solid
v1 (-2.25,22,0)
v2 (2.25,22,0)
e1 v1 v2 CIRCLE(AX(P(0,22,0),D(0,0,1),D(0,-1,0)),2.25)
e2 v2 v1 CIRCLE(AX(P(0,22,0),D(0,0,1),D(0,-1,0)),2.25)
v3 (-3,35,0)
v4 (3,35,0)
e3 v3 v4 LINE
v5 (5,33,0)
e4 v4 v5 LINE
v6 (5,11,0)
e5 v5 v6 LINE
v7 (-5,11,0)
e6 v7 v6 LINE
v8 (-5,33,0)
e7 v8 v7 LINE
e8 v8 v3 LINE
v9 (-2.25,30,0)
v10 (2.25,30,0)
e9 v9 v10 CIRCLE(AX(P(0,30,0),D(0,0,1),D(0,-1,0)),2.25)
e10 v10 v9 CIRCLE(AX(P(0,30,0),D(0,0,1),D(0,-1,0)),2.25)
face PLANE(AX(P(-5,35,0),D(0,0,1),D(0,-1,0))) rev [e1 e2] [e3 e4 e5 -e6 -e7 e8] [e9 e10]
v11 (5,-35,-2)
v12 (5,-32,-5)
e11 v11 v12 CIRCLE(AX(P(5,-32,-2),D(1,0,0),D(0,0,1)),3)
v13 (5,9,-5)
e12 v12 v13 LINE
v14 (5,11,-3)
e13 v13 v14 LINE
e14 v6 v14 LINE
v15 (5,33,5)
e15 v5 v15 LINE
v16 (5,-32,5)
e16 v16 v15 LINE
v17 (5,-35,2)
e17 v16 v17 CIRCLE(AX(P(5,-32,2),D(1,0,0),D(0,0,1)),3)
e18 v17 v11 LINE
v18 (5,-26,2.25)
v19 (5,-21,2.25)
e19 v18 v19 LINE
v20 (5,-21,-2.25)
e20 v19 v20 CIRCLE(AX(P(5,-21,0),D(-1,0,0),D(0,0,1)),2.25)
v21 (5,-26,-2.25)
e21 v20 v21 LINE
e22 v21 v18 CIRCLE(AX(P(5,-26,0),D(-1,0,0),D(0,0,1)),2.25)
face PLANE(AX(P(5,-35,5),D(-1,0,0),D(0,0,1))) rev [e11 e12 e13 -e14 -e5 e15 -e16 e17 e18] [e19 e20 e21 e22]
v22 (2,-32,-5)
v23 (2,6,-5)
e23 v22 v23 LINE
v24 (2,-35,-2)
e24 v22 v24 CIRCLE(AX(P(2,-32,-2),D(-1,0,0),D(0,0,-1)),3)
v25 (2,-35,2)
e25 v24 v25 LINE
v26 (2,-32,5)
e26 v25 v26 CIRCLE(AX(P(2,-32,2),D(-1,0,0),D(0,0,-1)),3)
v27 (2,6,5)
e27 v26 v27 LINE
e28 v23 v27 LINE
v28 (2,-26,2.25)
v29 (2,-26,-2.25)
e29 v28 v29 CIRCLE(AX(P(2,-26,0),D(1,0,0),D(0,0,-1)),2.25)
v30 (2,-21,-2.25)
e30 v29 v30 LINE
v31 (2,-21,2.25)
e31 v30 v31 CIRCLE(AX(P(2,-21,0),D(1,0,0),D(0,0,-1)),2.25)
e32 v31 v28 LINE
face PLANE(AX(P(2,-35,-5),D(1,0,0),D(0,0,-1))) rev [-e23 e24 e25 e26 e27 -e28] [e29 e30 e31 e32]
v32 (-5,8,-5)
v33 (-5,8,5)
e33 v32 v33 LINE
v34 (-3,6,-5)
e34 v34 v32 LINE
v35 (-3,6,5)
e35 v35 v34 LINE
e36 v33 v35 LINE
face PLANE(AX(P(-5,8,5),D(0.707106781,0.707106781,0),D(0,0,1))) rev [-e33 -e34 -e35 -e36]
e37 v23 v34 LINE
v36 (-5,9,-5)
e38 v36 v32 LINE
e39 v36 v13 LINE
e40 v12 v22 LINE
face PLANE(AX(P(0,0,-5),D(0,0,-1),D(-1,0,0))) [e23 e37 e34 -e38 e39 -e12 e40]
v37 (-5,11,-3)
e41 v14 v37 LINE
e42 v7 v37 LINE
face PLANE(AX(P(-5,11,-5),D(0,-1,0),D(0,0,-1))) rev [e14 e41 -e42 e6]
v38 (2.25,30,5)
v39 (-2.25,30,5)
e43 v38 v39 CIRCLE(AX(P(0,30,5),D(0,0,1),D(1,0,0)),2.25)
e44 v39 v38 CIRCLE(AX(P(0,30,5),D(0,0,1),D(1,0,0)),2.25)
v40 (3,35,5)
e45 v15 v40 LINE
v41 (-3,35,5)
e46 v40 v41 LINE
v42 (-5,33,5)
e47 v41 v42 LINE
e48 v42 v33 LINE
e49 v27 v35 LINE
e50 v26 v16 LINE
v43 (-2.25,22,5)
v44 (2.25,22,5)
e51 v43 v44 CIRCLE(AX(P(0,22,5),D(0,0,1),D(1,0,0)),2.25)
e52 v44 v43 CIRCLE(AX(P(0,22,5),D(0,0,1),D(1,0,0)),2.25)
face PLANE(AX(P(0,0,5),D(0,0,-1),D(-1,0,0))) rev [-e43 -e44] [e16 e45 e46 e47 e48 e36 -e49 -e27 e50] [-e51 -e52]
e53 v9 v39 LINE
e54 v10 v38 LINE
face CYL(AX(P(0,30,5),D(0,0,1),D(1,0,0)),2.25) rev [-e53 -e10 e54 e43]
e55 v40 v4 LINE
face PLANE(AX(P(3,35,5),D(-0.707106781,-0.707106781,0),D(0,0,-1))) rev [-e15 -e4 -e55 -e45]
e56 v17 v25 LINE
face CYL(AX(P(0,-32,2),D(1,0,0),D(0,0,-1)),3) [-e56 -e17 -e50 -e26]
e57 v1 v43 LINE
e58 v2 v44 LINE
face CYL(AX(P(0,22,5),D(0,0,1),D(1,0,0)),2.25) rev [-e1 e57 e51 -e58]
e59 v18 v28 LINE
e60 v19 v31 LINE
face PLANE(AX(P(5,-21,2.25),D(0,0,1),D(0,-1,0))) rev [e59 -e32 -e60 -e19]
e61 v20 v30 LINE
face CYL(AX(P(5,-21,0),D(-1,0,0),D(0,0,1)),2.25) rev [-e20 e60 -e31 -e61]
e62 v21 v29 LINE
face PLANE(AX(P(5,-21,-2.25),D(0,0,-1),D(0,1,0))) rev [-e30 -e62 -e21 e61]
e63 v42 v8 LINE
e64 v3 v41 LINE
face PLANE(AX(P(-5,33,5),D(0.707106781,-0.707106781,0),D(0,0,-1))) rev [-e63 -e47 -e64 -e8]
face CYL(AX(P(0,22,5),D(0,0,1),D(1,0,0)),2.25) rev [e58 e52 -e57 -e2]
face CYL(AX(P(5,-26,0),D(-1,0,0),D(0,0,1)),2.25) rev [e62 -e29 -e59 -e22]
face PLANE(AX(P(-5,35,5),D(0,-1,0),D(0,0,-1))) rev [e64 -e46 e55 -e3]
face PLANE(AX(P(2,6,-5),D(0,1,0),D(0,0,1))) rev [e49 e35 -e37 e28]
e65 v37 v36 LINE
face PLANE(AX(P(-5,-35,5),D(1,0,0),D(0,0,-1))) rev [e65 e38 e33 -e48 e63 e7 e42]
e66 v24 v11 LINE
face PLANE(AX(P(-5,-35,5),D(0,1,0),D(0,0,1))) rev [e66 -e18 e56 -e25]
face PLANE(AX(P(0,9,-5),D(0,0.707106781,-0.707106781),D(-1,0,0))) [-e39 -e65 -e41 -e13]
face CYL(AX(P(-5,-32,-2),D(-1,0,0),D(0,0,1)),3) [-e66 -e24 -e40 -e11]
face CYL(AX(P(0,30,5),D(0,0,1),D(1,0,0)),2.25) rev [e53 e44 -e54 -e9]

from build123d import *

# Parameters (mm, degrees)
SKETCH1_W            = 10
SKETCH1_H            = 70
BOSS_EXTRUDE1_DEPTH  = 5
SKETCH2_W            = 7
SKETCH2_H            = 41
CUT_EXTRUDE1_DEPTH   = 37.742346142
SKETCH3_W            = 5
SKETCH3_H            = 24
CUT_EXTRUDE2_DEPTH   = 37.742346142
CUT_EXTRUDE3_DEPTH   = 37.742346142
FILLET1_R            = 3
M4_CLEARANCE_HOLE1_D = 4.5
CHAMFER1_SIZE        = 2


with BuildPart() as part:
    # Sketch1 → Boss-Extrude1 (new, symmetric)
    with BuildSketch(Plane.XY):
        Rectangle(SKETCH1_W, SKETCH1_H)
    extrude(amount=BOSS_EXTRUDE1_DEPTH, both=True)

    # Sketch2 → Cut-Extrude1 (cut, through all)
    with BuildSketch(Plane.XY.offset(5)):
        with Locations((-1.5, -14.5)):
            Rectangle(SKETCH2_W, SKETCH2_H)
    extrude(amount=-CUT_EXTRUDE1_DEPTH, mode=Mode.SUBTRACT)

    # Sketch3 → Cut-Extrude2 (cut, through all)
    with BuildSketch(Plane(origin=(5, 0, 0), x_dir=(0, 0, -1), z_dir=(1, 0, 0))):
        with Locations((2.5, 23)):
            Rectangle(SKETCH3_W, SKETCH3_H)
    extrude(amount=-CUT_EXTRUDE2_DEPTH, mode=Mode.SUBTRACT)

    # Sketch4 → Cut-Extrude3 (cut, through all)
    with BuildSketch(Plane.ZY.offset(5)):
        with BuildLine():
            Line((2.25, -21), (2.25, -26))
            ThreePointArc((2.25, -26), (0, -28.25), (-2.25, -26))
            Line((-2.25, -26), (-2.25, -21))
            ThreePointArc((-2.25, -21), (0, -18.75), (2.25, -21))
        make_face()
    extrude(amount=-CUT_EXTRUDE3_DEPTH, mode=Mode.SUBTRACT)

    # Fillet1
    fillet1_edges = [part.edges().sort_by_distance(p)[0] for p in [
        (3.5, -35, -5),
        (3.5, -35, 5),
    ]]
    fillet(fillet1_edges, radius=FILLET1_R)

    # M4 Clearance Hole1 (through all)
    with Locations(Plane.XY.offset(5)):
        with Locations((0, 30), (0, 22)):
            Hole(M4_CLEARANCE_HOLE1_D / 2)

    # Chamfer1
    chamfer1_edges = [part.edges().sort_by_distance(p)[0] for p in [
        (-5, 6, 0),
        (0, 11, -5),
        (-5, 35, 2.5),
        (5, 35, 2.5),
    ]]
    chamfer(chamfer1_edges, length=CHAMFER1_SIZE)


solid = part.part
